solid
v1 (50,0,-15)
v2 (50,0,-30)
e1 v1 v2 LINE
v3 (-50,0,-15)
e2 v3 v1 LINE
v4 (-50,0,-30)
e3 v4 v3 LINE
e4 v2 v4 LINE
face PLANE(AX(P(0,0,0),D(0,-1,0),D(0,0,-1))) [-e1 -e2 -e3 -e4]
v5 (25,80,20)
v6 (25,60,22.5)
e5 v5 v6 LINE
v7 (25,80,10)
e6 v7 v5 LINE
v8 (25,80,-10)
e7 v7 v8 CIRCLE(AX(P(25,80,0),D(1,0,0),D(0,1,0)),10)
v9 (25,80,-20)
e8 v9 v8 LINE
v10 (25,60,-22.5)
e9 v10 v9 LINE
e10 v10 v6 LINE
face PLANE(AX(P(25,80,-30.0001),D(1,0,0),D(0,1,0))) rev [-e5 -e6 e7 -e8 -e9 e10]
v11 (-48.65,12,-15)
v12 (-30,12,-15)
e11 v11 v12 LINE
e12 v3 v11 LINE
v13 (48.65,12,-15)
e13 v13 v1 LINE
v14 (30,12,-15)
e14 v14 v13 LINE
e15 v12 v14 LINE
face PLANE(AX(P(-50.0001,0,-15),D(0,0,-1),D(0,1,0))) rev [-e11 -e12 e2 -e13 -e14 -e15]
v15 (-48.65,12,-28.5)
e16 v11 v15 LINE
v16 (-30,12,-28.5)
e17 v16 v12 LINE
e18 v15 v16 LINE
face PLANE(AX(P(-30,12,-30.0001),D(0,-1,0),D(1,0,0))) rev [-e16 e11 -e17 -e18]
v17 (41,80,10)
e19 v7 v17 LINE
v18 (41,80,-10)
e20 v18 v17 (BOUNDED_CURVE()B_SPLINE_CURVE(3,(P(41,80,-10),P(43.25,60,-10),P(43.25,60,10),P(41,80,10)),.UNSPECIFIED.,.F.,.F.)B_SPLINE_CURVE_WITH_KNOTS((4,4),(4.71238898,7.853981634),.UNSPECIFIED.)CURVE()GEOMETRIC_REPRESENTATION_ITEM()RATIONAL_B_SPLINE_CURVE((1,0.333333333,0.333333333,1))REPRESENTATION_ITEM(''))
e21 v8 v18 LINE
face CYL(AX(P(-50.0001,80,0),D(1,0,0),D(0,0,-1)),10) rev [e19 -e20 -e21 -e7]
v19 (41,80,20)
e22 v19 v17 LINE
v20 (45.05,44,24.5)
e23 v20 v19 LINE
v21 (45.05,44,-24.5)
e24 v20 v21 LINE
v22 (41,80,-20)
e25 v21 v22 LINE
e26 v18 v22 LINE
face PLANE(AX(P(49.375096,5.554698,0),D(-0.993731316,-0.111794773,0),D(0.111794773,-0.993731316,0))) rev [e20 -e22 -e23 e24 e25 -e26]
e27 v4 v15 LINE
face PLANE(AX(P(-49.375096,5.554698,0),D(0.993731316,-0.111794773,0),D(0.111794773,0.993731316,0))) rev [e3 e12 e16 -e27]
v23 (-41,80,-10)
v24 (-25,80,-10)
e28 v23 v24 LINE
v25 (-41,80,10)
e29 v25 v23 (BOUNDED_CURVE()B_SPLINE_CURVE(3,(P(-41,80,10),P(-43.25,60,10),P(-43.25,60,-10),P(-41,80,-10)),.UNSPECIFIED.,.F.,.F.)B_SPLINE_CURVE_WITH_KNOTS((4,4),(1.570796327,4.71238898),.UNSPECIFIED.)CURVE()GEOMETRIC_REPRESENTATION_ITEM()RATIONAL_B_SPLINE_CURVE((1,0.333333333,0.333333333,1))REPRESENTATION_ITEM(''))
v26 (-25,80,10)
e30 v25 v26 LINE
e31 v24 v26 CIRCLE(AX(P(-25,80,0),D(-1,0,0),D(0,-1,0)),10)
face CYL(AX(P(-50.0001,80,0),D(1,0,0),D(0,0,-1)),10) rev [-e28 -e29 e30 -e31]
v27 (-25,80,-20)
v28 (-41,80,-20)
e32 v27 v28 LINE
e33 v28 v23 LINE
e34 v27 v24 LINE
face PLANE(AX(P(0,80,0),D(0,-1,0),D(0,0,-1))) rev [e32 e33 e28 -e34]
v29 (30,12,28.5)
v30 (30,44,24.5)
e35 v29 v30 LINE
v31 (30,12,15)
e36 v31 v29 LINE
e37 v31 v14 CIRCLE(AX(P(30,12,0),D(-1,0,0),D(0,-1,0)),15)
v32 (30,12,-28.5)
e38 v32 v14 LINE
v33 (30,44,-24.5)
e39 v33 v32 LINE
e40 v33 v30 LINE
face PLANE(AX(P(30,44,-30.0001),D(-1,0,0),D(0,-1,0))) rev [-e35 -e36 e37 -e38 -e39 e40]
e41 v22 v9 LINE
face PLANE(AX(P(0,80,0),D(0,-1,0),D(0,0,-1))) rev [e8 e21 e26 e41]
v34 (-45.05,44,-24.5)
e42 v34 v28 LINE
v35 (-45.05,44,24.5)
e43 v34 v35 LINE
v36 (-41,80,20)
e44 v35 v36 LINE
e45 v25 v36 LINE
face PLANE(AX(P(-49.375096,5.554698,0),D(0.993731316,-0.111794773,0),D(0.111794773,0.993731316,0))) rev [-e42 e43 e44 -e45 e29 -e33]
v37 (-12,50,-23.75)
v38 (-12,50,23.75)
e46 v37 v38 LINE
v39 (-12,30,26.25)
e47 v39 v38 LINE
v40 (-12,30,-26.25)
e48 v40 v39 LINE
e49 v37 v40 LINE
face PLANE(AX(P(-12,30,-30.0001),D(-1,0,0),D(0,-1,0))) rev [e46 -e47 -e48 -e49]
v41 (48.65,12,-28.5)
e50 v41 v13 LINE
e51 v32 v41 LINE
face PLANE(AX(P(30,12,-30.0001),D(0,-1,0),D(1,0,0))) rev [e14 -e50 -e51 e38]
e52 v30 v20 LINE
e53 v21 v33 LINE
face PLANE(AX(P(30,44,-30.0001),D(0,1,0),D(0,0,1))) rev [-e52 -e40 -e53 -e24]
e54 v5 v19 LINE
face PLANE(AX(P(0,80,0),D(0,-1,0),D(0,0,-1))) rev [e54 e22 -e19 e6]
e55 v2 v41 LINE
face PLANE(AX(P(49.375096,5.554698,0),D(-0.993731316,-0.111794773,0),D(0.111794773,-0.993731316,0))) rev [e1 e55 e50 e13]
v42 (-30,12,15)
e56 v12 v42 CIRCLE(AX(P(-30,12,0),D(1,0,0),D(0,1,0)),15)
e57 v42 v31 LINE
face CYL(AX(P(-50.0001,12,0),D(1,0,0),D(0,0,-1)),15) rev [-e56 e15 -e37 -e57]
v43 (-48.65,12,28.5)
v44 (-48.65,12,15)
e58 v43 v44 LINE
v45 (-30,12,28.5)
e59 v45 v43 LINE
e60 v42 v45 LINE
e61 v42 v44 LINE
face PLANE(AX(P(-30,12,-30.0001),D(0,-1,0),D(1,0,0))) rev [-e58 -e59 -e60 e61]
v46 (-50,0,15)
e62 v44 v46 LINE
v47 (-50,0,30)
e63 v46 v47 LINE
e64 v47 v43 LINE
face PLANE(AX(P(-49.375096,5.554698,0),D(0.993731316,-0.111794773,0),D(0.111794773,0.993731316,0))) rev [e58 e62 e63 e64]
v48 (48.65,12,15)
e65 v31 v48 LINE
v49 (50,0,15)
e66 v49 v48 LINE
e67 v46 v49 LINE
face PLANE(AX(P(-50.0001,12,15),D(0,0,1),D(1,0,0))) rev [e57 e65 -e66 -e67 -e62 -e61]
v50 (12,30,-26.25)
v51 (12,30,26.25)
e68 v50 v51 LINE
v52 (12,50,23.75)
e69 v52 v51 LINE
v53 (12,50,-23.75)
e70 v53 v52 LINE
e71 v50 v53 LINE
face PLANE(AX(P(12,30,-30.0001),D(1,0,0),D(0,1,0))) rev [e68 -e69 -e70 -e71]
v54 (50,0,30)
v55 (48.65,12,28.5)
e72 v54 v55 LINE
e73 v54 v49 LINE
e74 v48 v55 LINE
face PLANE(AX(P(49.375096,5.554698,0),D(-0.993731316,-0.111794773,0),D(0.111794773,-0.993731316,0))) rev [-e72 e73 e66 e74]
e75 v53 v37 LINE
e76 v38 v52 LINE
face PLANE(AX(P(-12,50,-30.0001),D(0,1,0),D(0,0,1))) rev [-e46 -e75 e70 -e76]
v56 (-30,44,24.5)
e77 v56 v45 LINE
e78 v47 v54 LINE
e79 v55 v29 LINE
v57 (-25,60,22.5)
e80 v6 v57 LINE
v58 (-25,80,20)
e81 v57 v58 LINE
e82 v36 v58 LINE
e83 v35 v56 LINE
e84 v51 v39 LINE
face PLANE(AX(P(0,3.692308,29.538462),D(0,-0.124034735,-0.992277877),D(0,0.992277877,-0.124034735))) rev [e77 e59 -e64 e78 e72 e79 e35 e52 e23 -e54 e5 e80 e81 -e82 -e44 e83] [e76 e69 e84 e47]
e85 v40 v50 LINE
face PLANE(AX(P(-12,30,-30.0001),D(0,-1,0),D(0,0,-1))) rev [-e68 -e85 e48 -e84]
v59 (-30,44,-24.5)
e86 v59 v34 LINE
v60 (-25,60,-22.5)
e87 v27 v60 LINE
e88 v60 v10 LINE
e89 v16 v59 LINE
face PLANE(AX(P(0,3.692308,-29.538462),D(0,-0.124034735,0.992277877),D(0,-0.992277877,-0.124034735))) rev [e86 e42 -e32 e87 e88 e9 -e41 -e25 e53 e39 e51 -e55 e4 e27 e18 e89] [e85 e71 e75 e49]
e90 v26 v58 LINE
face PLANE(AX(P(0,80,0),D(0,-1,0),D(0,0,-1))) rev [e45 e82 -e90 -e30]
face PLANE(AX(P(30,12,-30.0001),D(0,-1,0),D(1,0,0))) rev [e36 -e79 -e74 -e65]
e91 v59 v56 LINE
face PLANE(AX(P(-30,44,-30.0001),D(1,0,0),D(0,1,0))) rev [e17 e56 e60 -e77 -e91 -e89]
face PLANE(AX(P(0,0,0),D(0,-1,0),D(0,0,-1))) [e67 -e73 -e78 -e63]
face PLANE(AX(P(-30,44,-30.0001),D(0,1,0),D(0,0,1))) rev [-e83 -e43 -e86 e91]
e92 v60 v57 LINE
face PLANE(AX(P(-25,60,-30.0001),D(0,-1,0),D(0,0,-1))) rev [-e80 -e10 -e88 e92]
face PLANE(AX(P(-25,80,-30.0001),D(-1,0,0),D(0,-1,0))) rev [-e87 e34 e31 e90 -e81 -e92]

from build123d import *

# Parameters (mm, degrees)
FEET_AND_UPRIGHTS_CUT_DEPTH          = 99.994949528
FEET_AND_UPRIGHTS_CUT_DEPTH_BACK     = 99.994949528
FEET_AND_UPRIGHTS_PROFILE_SKETCH_W   = 29.409363616
FEET_AND_UPRIGHTS_PROFILE_SKETCH_H   = 32
FEET_AND_UPRIGHTS_PROFILE_SKETCH_W_2 = 50
FEET_AND_UPRIGHTS_PROFILE_SKETCH_H_2 = 20
BASE_ARCH_CUT_DEPTH                  = 99.994949528
BASE_ARCH_CUT_DEPTH_BACK             = 99.994949528
CRADLE_SADDLES_CUT_DEPTH             = 99.994949528
CRADLE_SADDLES_CUT_DEPTH_BACK        = 99.994949528
WEB_WINDOW_CUT_DEPTH                 = 99.994949528
WEB_WINDOW_CUT_DEPTH_BACK            = 99.994949528
WEB_WINDOW_SKETCH_W                  = 24
WEB_WINDOW_SKETCH_H                  = 20


with BuildPart() as part:
    # Base Profile Sketch → Tapered Block Loft section 0
    with BuildSketch(Plane(origin=(0, 0, 0), x_dir=(1, 0, 0), z_dir=(0, 1, 0))):
        with BuildLine():
            Line((-50, -30), (50, -30))
            Line((50, -30), (50, 30))
            Line((50, 30), (-50, 30))
            Line((-50, 30), (-50, -30))
        make_face()
    # Top Profile Sketch → Tapered Block Loft section 1
    with BuildSketch(Plane(origin=(0, 80, 0), x_dir=(1, 0, 0), z_dir=(0, 1, 0))):
        with BuildLine():
            Line((-41, -20), (41, -20))
            Line((41, -20), (41, 20))
            Line((41, 20), (-41, 20))
            Line((-41, 20), (-41, -20))
        make_face()
    loft()

    # Feet and Uprights Profile Sketch → Feet and Uprights Cut (cut, two sides: drawn at the far end of the back side and taken through both)
    with BuildSketch(Plane.XY.offset(-FEET_AND_UPRIGHTS_CUT_DEPTH_BACK)):
        with Locations((-44.704681808, 28)):
            Rectangle(FEET_AND_UPRIGHTS_PROFILE_SKETCH_W, FEET_AND_UPRIGHTS_PROFILE_SKETCH_H)
        with Locations((0, 70)):
            Rectangle(FEET_AND_UPRIGHTS_PROFILE_SKETCH_W_2, FEET_AND_UPRIGHTS_PROFILE_SKETCH_H_2)
        with Locations((44.704681808, 28)):
            Rectangle(FEET_AND_UPRIGHTS_PROFILE_SKETCH_W, FEET_AND_UPRIGHTS_PROFILE_SKETCH_H)
    extrude(amount=FEET_AND_UPRIGHTS_CUT_DEPTH + FEET_AND_UPRIGHTS_CUT_DEPTH_BACK, mode=Mode.SUBTRACT)

    # Base Arch Sketch → Base Arch Cut (cut, two sides: drawn at the far end of the back side and taken through both)
    with BuildSketch(Plane(origin=(0, 0, 0), x_dir=(0, 0, -1), z_dir=(1, 0, 0)).offset(-BASE_ARCH_CUT_DEPTH_BACK)):
        with BuildLine():
            Line((-10, 80), (10, 80))
            ThreePointArc((10, 80), (0, 70), (-10, 80))
        make_face()
    extrude(amount=BASE_ARCH_CUT_DEPTH + BASE_ARCH_CUT_DEPTH_BACK, mode=Mode.SUBTRACT)

    # Cradle Saddles Sketch → Cradle Saddles Cut (cut, two sides: drawn at the far end of the back side and taken through both)
    with BuildSketch(Plane(origin=(0, 0, 0), x_dir=(0, 0, -1), z_dir=(1, 0, 0)).offset(-CRADLE_SADDLES_CUT_DEPTH_BACK)):
        with BuildLine():
            Line((-15, 12), (-15, 0))
            Line((-15, 0), (15, 0))
            Line((15, 0), (15, 12))
            ThreePointArc((15, 12), (0, 27), (-15, 12))
        make_face()
    extrude(amount=CRADLE_SADDLES_CUT_DEPTH + CRADLE_SADDLES_CUT_DEPTH_BACK, mode=Mode.SUBTRACT)

    # Web Window Sketch → Web Window Cut (cut, two sides: drawn at the far end of the back side and taken through both)
    with BuildSketch(Plane.XY.offset(-WEB_WINDOW_CUT_DEPTH_BACK)):
        with Locations((0, 40)):
            Rectangle(WEB_WINDOW_SKETCH_W, WEB_WINDOW_SKETCH_H)
    extrude(amount=WEB_WINDOW_CUT_DEPTH + WEB_WINDOW_CUT_DEPTH_BACK, mode=Mode.SUBTRACT)


solid = part.part
